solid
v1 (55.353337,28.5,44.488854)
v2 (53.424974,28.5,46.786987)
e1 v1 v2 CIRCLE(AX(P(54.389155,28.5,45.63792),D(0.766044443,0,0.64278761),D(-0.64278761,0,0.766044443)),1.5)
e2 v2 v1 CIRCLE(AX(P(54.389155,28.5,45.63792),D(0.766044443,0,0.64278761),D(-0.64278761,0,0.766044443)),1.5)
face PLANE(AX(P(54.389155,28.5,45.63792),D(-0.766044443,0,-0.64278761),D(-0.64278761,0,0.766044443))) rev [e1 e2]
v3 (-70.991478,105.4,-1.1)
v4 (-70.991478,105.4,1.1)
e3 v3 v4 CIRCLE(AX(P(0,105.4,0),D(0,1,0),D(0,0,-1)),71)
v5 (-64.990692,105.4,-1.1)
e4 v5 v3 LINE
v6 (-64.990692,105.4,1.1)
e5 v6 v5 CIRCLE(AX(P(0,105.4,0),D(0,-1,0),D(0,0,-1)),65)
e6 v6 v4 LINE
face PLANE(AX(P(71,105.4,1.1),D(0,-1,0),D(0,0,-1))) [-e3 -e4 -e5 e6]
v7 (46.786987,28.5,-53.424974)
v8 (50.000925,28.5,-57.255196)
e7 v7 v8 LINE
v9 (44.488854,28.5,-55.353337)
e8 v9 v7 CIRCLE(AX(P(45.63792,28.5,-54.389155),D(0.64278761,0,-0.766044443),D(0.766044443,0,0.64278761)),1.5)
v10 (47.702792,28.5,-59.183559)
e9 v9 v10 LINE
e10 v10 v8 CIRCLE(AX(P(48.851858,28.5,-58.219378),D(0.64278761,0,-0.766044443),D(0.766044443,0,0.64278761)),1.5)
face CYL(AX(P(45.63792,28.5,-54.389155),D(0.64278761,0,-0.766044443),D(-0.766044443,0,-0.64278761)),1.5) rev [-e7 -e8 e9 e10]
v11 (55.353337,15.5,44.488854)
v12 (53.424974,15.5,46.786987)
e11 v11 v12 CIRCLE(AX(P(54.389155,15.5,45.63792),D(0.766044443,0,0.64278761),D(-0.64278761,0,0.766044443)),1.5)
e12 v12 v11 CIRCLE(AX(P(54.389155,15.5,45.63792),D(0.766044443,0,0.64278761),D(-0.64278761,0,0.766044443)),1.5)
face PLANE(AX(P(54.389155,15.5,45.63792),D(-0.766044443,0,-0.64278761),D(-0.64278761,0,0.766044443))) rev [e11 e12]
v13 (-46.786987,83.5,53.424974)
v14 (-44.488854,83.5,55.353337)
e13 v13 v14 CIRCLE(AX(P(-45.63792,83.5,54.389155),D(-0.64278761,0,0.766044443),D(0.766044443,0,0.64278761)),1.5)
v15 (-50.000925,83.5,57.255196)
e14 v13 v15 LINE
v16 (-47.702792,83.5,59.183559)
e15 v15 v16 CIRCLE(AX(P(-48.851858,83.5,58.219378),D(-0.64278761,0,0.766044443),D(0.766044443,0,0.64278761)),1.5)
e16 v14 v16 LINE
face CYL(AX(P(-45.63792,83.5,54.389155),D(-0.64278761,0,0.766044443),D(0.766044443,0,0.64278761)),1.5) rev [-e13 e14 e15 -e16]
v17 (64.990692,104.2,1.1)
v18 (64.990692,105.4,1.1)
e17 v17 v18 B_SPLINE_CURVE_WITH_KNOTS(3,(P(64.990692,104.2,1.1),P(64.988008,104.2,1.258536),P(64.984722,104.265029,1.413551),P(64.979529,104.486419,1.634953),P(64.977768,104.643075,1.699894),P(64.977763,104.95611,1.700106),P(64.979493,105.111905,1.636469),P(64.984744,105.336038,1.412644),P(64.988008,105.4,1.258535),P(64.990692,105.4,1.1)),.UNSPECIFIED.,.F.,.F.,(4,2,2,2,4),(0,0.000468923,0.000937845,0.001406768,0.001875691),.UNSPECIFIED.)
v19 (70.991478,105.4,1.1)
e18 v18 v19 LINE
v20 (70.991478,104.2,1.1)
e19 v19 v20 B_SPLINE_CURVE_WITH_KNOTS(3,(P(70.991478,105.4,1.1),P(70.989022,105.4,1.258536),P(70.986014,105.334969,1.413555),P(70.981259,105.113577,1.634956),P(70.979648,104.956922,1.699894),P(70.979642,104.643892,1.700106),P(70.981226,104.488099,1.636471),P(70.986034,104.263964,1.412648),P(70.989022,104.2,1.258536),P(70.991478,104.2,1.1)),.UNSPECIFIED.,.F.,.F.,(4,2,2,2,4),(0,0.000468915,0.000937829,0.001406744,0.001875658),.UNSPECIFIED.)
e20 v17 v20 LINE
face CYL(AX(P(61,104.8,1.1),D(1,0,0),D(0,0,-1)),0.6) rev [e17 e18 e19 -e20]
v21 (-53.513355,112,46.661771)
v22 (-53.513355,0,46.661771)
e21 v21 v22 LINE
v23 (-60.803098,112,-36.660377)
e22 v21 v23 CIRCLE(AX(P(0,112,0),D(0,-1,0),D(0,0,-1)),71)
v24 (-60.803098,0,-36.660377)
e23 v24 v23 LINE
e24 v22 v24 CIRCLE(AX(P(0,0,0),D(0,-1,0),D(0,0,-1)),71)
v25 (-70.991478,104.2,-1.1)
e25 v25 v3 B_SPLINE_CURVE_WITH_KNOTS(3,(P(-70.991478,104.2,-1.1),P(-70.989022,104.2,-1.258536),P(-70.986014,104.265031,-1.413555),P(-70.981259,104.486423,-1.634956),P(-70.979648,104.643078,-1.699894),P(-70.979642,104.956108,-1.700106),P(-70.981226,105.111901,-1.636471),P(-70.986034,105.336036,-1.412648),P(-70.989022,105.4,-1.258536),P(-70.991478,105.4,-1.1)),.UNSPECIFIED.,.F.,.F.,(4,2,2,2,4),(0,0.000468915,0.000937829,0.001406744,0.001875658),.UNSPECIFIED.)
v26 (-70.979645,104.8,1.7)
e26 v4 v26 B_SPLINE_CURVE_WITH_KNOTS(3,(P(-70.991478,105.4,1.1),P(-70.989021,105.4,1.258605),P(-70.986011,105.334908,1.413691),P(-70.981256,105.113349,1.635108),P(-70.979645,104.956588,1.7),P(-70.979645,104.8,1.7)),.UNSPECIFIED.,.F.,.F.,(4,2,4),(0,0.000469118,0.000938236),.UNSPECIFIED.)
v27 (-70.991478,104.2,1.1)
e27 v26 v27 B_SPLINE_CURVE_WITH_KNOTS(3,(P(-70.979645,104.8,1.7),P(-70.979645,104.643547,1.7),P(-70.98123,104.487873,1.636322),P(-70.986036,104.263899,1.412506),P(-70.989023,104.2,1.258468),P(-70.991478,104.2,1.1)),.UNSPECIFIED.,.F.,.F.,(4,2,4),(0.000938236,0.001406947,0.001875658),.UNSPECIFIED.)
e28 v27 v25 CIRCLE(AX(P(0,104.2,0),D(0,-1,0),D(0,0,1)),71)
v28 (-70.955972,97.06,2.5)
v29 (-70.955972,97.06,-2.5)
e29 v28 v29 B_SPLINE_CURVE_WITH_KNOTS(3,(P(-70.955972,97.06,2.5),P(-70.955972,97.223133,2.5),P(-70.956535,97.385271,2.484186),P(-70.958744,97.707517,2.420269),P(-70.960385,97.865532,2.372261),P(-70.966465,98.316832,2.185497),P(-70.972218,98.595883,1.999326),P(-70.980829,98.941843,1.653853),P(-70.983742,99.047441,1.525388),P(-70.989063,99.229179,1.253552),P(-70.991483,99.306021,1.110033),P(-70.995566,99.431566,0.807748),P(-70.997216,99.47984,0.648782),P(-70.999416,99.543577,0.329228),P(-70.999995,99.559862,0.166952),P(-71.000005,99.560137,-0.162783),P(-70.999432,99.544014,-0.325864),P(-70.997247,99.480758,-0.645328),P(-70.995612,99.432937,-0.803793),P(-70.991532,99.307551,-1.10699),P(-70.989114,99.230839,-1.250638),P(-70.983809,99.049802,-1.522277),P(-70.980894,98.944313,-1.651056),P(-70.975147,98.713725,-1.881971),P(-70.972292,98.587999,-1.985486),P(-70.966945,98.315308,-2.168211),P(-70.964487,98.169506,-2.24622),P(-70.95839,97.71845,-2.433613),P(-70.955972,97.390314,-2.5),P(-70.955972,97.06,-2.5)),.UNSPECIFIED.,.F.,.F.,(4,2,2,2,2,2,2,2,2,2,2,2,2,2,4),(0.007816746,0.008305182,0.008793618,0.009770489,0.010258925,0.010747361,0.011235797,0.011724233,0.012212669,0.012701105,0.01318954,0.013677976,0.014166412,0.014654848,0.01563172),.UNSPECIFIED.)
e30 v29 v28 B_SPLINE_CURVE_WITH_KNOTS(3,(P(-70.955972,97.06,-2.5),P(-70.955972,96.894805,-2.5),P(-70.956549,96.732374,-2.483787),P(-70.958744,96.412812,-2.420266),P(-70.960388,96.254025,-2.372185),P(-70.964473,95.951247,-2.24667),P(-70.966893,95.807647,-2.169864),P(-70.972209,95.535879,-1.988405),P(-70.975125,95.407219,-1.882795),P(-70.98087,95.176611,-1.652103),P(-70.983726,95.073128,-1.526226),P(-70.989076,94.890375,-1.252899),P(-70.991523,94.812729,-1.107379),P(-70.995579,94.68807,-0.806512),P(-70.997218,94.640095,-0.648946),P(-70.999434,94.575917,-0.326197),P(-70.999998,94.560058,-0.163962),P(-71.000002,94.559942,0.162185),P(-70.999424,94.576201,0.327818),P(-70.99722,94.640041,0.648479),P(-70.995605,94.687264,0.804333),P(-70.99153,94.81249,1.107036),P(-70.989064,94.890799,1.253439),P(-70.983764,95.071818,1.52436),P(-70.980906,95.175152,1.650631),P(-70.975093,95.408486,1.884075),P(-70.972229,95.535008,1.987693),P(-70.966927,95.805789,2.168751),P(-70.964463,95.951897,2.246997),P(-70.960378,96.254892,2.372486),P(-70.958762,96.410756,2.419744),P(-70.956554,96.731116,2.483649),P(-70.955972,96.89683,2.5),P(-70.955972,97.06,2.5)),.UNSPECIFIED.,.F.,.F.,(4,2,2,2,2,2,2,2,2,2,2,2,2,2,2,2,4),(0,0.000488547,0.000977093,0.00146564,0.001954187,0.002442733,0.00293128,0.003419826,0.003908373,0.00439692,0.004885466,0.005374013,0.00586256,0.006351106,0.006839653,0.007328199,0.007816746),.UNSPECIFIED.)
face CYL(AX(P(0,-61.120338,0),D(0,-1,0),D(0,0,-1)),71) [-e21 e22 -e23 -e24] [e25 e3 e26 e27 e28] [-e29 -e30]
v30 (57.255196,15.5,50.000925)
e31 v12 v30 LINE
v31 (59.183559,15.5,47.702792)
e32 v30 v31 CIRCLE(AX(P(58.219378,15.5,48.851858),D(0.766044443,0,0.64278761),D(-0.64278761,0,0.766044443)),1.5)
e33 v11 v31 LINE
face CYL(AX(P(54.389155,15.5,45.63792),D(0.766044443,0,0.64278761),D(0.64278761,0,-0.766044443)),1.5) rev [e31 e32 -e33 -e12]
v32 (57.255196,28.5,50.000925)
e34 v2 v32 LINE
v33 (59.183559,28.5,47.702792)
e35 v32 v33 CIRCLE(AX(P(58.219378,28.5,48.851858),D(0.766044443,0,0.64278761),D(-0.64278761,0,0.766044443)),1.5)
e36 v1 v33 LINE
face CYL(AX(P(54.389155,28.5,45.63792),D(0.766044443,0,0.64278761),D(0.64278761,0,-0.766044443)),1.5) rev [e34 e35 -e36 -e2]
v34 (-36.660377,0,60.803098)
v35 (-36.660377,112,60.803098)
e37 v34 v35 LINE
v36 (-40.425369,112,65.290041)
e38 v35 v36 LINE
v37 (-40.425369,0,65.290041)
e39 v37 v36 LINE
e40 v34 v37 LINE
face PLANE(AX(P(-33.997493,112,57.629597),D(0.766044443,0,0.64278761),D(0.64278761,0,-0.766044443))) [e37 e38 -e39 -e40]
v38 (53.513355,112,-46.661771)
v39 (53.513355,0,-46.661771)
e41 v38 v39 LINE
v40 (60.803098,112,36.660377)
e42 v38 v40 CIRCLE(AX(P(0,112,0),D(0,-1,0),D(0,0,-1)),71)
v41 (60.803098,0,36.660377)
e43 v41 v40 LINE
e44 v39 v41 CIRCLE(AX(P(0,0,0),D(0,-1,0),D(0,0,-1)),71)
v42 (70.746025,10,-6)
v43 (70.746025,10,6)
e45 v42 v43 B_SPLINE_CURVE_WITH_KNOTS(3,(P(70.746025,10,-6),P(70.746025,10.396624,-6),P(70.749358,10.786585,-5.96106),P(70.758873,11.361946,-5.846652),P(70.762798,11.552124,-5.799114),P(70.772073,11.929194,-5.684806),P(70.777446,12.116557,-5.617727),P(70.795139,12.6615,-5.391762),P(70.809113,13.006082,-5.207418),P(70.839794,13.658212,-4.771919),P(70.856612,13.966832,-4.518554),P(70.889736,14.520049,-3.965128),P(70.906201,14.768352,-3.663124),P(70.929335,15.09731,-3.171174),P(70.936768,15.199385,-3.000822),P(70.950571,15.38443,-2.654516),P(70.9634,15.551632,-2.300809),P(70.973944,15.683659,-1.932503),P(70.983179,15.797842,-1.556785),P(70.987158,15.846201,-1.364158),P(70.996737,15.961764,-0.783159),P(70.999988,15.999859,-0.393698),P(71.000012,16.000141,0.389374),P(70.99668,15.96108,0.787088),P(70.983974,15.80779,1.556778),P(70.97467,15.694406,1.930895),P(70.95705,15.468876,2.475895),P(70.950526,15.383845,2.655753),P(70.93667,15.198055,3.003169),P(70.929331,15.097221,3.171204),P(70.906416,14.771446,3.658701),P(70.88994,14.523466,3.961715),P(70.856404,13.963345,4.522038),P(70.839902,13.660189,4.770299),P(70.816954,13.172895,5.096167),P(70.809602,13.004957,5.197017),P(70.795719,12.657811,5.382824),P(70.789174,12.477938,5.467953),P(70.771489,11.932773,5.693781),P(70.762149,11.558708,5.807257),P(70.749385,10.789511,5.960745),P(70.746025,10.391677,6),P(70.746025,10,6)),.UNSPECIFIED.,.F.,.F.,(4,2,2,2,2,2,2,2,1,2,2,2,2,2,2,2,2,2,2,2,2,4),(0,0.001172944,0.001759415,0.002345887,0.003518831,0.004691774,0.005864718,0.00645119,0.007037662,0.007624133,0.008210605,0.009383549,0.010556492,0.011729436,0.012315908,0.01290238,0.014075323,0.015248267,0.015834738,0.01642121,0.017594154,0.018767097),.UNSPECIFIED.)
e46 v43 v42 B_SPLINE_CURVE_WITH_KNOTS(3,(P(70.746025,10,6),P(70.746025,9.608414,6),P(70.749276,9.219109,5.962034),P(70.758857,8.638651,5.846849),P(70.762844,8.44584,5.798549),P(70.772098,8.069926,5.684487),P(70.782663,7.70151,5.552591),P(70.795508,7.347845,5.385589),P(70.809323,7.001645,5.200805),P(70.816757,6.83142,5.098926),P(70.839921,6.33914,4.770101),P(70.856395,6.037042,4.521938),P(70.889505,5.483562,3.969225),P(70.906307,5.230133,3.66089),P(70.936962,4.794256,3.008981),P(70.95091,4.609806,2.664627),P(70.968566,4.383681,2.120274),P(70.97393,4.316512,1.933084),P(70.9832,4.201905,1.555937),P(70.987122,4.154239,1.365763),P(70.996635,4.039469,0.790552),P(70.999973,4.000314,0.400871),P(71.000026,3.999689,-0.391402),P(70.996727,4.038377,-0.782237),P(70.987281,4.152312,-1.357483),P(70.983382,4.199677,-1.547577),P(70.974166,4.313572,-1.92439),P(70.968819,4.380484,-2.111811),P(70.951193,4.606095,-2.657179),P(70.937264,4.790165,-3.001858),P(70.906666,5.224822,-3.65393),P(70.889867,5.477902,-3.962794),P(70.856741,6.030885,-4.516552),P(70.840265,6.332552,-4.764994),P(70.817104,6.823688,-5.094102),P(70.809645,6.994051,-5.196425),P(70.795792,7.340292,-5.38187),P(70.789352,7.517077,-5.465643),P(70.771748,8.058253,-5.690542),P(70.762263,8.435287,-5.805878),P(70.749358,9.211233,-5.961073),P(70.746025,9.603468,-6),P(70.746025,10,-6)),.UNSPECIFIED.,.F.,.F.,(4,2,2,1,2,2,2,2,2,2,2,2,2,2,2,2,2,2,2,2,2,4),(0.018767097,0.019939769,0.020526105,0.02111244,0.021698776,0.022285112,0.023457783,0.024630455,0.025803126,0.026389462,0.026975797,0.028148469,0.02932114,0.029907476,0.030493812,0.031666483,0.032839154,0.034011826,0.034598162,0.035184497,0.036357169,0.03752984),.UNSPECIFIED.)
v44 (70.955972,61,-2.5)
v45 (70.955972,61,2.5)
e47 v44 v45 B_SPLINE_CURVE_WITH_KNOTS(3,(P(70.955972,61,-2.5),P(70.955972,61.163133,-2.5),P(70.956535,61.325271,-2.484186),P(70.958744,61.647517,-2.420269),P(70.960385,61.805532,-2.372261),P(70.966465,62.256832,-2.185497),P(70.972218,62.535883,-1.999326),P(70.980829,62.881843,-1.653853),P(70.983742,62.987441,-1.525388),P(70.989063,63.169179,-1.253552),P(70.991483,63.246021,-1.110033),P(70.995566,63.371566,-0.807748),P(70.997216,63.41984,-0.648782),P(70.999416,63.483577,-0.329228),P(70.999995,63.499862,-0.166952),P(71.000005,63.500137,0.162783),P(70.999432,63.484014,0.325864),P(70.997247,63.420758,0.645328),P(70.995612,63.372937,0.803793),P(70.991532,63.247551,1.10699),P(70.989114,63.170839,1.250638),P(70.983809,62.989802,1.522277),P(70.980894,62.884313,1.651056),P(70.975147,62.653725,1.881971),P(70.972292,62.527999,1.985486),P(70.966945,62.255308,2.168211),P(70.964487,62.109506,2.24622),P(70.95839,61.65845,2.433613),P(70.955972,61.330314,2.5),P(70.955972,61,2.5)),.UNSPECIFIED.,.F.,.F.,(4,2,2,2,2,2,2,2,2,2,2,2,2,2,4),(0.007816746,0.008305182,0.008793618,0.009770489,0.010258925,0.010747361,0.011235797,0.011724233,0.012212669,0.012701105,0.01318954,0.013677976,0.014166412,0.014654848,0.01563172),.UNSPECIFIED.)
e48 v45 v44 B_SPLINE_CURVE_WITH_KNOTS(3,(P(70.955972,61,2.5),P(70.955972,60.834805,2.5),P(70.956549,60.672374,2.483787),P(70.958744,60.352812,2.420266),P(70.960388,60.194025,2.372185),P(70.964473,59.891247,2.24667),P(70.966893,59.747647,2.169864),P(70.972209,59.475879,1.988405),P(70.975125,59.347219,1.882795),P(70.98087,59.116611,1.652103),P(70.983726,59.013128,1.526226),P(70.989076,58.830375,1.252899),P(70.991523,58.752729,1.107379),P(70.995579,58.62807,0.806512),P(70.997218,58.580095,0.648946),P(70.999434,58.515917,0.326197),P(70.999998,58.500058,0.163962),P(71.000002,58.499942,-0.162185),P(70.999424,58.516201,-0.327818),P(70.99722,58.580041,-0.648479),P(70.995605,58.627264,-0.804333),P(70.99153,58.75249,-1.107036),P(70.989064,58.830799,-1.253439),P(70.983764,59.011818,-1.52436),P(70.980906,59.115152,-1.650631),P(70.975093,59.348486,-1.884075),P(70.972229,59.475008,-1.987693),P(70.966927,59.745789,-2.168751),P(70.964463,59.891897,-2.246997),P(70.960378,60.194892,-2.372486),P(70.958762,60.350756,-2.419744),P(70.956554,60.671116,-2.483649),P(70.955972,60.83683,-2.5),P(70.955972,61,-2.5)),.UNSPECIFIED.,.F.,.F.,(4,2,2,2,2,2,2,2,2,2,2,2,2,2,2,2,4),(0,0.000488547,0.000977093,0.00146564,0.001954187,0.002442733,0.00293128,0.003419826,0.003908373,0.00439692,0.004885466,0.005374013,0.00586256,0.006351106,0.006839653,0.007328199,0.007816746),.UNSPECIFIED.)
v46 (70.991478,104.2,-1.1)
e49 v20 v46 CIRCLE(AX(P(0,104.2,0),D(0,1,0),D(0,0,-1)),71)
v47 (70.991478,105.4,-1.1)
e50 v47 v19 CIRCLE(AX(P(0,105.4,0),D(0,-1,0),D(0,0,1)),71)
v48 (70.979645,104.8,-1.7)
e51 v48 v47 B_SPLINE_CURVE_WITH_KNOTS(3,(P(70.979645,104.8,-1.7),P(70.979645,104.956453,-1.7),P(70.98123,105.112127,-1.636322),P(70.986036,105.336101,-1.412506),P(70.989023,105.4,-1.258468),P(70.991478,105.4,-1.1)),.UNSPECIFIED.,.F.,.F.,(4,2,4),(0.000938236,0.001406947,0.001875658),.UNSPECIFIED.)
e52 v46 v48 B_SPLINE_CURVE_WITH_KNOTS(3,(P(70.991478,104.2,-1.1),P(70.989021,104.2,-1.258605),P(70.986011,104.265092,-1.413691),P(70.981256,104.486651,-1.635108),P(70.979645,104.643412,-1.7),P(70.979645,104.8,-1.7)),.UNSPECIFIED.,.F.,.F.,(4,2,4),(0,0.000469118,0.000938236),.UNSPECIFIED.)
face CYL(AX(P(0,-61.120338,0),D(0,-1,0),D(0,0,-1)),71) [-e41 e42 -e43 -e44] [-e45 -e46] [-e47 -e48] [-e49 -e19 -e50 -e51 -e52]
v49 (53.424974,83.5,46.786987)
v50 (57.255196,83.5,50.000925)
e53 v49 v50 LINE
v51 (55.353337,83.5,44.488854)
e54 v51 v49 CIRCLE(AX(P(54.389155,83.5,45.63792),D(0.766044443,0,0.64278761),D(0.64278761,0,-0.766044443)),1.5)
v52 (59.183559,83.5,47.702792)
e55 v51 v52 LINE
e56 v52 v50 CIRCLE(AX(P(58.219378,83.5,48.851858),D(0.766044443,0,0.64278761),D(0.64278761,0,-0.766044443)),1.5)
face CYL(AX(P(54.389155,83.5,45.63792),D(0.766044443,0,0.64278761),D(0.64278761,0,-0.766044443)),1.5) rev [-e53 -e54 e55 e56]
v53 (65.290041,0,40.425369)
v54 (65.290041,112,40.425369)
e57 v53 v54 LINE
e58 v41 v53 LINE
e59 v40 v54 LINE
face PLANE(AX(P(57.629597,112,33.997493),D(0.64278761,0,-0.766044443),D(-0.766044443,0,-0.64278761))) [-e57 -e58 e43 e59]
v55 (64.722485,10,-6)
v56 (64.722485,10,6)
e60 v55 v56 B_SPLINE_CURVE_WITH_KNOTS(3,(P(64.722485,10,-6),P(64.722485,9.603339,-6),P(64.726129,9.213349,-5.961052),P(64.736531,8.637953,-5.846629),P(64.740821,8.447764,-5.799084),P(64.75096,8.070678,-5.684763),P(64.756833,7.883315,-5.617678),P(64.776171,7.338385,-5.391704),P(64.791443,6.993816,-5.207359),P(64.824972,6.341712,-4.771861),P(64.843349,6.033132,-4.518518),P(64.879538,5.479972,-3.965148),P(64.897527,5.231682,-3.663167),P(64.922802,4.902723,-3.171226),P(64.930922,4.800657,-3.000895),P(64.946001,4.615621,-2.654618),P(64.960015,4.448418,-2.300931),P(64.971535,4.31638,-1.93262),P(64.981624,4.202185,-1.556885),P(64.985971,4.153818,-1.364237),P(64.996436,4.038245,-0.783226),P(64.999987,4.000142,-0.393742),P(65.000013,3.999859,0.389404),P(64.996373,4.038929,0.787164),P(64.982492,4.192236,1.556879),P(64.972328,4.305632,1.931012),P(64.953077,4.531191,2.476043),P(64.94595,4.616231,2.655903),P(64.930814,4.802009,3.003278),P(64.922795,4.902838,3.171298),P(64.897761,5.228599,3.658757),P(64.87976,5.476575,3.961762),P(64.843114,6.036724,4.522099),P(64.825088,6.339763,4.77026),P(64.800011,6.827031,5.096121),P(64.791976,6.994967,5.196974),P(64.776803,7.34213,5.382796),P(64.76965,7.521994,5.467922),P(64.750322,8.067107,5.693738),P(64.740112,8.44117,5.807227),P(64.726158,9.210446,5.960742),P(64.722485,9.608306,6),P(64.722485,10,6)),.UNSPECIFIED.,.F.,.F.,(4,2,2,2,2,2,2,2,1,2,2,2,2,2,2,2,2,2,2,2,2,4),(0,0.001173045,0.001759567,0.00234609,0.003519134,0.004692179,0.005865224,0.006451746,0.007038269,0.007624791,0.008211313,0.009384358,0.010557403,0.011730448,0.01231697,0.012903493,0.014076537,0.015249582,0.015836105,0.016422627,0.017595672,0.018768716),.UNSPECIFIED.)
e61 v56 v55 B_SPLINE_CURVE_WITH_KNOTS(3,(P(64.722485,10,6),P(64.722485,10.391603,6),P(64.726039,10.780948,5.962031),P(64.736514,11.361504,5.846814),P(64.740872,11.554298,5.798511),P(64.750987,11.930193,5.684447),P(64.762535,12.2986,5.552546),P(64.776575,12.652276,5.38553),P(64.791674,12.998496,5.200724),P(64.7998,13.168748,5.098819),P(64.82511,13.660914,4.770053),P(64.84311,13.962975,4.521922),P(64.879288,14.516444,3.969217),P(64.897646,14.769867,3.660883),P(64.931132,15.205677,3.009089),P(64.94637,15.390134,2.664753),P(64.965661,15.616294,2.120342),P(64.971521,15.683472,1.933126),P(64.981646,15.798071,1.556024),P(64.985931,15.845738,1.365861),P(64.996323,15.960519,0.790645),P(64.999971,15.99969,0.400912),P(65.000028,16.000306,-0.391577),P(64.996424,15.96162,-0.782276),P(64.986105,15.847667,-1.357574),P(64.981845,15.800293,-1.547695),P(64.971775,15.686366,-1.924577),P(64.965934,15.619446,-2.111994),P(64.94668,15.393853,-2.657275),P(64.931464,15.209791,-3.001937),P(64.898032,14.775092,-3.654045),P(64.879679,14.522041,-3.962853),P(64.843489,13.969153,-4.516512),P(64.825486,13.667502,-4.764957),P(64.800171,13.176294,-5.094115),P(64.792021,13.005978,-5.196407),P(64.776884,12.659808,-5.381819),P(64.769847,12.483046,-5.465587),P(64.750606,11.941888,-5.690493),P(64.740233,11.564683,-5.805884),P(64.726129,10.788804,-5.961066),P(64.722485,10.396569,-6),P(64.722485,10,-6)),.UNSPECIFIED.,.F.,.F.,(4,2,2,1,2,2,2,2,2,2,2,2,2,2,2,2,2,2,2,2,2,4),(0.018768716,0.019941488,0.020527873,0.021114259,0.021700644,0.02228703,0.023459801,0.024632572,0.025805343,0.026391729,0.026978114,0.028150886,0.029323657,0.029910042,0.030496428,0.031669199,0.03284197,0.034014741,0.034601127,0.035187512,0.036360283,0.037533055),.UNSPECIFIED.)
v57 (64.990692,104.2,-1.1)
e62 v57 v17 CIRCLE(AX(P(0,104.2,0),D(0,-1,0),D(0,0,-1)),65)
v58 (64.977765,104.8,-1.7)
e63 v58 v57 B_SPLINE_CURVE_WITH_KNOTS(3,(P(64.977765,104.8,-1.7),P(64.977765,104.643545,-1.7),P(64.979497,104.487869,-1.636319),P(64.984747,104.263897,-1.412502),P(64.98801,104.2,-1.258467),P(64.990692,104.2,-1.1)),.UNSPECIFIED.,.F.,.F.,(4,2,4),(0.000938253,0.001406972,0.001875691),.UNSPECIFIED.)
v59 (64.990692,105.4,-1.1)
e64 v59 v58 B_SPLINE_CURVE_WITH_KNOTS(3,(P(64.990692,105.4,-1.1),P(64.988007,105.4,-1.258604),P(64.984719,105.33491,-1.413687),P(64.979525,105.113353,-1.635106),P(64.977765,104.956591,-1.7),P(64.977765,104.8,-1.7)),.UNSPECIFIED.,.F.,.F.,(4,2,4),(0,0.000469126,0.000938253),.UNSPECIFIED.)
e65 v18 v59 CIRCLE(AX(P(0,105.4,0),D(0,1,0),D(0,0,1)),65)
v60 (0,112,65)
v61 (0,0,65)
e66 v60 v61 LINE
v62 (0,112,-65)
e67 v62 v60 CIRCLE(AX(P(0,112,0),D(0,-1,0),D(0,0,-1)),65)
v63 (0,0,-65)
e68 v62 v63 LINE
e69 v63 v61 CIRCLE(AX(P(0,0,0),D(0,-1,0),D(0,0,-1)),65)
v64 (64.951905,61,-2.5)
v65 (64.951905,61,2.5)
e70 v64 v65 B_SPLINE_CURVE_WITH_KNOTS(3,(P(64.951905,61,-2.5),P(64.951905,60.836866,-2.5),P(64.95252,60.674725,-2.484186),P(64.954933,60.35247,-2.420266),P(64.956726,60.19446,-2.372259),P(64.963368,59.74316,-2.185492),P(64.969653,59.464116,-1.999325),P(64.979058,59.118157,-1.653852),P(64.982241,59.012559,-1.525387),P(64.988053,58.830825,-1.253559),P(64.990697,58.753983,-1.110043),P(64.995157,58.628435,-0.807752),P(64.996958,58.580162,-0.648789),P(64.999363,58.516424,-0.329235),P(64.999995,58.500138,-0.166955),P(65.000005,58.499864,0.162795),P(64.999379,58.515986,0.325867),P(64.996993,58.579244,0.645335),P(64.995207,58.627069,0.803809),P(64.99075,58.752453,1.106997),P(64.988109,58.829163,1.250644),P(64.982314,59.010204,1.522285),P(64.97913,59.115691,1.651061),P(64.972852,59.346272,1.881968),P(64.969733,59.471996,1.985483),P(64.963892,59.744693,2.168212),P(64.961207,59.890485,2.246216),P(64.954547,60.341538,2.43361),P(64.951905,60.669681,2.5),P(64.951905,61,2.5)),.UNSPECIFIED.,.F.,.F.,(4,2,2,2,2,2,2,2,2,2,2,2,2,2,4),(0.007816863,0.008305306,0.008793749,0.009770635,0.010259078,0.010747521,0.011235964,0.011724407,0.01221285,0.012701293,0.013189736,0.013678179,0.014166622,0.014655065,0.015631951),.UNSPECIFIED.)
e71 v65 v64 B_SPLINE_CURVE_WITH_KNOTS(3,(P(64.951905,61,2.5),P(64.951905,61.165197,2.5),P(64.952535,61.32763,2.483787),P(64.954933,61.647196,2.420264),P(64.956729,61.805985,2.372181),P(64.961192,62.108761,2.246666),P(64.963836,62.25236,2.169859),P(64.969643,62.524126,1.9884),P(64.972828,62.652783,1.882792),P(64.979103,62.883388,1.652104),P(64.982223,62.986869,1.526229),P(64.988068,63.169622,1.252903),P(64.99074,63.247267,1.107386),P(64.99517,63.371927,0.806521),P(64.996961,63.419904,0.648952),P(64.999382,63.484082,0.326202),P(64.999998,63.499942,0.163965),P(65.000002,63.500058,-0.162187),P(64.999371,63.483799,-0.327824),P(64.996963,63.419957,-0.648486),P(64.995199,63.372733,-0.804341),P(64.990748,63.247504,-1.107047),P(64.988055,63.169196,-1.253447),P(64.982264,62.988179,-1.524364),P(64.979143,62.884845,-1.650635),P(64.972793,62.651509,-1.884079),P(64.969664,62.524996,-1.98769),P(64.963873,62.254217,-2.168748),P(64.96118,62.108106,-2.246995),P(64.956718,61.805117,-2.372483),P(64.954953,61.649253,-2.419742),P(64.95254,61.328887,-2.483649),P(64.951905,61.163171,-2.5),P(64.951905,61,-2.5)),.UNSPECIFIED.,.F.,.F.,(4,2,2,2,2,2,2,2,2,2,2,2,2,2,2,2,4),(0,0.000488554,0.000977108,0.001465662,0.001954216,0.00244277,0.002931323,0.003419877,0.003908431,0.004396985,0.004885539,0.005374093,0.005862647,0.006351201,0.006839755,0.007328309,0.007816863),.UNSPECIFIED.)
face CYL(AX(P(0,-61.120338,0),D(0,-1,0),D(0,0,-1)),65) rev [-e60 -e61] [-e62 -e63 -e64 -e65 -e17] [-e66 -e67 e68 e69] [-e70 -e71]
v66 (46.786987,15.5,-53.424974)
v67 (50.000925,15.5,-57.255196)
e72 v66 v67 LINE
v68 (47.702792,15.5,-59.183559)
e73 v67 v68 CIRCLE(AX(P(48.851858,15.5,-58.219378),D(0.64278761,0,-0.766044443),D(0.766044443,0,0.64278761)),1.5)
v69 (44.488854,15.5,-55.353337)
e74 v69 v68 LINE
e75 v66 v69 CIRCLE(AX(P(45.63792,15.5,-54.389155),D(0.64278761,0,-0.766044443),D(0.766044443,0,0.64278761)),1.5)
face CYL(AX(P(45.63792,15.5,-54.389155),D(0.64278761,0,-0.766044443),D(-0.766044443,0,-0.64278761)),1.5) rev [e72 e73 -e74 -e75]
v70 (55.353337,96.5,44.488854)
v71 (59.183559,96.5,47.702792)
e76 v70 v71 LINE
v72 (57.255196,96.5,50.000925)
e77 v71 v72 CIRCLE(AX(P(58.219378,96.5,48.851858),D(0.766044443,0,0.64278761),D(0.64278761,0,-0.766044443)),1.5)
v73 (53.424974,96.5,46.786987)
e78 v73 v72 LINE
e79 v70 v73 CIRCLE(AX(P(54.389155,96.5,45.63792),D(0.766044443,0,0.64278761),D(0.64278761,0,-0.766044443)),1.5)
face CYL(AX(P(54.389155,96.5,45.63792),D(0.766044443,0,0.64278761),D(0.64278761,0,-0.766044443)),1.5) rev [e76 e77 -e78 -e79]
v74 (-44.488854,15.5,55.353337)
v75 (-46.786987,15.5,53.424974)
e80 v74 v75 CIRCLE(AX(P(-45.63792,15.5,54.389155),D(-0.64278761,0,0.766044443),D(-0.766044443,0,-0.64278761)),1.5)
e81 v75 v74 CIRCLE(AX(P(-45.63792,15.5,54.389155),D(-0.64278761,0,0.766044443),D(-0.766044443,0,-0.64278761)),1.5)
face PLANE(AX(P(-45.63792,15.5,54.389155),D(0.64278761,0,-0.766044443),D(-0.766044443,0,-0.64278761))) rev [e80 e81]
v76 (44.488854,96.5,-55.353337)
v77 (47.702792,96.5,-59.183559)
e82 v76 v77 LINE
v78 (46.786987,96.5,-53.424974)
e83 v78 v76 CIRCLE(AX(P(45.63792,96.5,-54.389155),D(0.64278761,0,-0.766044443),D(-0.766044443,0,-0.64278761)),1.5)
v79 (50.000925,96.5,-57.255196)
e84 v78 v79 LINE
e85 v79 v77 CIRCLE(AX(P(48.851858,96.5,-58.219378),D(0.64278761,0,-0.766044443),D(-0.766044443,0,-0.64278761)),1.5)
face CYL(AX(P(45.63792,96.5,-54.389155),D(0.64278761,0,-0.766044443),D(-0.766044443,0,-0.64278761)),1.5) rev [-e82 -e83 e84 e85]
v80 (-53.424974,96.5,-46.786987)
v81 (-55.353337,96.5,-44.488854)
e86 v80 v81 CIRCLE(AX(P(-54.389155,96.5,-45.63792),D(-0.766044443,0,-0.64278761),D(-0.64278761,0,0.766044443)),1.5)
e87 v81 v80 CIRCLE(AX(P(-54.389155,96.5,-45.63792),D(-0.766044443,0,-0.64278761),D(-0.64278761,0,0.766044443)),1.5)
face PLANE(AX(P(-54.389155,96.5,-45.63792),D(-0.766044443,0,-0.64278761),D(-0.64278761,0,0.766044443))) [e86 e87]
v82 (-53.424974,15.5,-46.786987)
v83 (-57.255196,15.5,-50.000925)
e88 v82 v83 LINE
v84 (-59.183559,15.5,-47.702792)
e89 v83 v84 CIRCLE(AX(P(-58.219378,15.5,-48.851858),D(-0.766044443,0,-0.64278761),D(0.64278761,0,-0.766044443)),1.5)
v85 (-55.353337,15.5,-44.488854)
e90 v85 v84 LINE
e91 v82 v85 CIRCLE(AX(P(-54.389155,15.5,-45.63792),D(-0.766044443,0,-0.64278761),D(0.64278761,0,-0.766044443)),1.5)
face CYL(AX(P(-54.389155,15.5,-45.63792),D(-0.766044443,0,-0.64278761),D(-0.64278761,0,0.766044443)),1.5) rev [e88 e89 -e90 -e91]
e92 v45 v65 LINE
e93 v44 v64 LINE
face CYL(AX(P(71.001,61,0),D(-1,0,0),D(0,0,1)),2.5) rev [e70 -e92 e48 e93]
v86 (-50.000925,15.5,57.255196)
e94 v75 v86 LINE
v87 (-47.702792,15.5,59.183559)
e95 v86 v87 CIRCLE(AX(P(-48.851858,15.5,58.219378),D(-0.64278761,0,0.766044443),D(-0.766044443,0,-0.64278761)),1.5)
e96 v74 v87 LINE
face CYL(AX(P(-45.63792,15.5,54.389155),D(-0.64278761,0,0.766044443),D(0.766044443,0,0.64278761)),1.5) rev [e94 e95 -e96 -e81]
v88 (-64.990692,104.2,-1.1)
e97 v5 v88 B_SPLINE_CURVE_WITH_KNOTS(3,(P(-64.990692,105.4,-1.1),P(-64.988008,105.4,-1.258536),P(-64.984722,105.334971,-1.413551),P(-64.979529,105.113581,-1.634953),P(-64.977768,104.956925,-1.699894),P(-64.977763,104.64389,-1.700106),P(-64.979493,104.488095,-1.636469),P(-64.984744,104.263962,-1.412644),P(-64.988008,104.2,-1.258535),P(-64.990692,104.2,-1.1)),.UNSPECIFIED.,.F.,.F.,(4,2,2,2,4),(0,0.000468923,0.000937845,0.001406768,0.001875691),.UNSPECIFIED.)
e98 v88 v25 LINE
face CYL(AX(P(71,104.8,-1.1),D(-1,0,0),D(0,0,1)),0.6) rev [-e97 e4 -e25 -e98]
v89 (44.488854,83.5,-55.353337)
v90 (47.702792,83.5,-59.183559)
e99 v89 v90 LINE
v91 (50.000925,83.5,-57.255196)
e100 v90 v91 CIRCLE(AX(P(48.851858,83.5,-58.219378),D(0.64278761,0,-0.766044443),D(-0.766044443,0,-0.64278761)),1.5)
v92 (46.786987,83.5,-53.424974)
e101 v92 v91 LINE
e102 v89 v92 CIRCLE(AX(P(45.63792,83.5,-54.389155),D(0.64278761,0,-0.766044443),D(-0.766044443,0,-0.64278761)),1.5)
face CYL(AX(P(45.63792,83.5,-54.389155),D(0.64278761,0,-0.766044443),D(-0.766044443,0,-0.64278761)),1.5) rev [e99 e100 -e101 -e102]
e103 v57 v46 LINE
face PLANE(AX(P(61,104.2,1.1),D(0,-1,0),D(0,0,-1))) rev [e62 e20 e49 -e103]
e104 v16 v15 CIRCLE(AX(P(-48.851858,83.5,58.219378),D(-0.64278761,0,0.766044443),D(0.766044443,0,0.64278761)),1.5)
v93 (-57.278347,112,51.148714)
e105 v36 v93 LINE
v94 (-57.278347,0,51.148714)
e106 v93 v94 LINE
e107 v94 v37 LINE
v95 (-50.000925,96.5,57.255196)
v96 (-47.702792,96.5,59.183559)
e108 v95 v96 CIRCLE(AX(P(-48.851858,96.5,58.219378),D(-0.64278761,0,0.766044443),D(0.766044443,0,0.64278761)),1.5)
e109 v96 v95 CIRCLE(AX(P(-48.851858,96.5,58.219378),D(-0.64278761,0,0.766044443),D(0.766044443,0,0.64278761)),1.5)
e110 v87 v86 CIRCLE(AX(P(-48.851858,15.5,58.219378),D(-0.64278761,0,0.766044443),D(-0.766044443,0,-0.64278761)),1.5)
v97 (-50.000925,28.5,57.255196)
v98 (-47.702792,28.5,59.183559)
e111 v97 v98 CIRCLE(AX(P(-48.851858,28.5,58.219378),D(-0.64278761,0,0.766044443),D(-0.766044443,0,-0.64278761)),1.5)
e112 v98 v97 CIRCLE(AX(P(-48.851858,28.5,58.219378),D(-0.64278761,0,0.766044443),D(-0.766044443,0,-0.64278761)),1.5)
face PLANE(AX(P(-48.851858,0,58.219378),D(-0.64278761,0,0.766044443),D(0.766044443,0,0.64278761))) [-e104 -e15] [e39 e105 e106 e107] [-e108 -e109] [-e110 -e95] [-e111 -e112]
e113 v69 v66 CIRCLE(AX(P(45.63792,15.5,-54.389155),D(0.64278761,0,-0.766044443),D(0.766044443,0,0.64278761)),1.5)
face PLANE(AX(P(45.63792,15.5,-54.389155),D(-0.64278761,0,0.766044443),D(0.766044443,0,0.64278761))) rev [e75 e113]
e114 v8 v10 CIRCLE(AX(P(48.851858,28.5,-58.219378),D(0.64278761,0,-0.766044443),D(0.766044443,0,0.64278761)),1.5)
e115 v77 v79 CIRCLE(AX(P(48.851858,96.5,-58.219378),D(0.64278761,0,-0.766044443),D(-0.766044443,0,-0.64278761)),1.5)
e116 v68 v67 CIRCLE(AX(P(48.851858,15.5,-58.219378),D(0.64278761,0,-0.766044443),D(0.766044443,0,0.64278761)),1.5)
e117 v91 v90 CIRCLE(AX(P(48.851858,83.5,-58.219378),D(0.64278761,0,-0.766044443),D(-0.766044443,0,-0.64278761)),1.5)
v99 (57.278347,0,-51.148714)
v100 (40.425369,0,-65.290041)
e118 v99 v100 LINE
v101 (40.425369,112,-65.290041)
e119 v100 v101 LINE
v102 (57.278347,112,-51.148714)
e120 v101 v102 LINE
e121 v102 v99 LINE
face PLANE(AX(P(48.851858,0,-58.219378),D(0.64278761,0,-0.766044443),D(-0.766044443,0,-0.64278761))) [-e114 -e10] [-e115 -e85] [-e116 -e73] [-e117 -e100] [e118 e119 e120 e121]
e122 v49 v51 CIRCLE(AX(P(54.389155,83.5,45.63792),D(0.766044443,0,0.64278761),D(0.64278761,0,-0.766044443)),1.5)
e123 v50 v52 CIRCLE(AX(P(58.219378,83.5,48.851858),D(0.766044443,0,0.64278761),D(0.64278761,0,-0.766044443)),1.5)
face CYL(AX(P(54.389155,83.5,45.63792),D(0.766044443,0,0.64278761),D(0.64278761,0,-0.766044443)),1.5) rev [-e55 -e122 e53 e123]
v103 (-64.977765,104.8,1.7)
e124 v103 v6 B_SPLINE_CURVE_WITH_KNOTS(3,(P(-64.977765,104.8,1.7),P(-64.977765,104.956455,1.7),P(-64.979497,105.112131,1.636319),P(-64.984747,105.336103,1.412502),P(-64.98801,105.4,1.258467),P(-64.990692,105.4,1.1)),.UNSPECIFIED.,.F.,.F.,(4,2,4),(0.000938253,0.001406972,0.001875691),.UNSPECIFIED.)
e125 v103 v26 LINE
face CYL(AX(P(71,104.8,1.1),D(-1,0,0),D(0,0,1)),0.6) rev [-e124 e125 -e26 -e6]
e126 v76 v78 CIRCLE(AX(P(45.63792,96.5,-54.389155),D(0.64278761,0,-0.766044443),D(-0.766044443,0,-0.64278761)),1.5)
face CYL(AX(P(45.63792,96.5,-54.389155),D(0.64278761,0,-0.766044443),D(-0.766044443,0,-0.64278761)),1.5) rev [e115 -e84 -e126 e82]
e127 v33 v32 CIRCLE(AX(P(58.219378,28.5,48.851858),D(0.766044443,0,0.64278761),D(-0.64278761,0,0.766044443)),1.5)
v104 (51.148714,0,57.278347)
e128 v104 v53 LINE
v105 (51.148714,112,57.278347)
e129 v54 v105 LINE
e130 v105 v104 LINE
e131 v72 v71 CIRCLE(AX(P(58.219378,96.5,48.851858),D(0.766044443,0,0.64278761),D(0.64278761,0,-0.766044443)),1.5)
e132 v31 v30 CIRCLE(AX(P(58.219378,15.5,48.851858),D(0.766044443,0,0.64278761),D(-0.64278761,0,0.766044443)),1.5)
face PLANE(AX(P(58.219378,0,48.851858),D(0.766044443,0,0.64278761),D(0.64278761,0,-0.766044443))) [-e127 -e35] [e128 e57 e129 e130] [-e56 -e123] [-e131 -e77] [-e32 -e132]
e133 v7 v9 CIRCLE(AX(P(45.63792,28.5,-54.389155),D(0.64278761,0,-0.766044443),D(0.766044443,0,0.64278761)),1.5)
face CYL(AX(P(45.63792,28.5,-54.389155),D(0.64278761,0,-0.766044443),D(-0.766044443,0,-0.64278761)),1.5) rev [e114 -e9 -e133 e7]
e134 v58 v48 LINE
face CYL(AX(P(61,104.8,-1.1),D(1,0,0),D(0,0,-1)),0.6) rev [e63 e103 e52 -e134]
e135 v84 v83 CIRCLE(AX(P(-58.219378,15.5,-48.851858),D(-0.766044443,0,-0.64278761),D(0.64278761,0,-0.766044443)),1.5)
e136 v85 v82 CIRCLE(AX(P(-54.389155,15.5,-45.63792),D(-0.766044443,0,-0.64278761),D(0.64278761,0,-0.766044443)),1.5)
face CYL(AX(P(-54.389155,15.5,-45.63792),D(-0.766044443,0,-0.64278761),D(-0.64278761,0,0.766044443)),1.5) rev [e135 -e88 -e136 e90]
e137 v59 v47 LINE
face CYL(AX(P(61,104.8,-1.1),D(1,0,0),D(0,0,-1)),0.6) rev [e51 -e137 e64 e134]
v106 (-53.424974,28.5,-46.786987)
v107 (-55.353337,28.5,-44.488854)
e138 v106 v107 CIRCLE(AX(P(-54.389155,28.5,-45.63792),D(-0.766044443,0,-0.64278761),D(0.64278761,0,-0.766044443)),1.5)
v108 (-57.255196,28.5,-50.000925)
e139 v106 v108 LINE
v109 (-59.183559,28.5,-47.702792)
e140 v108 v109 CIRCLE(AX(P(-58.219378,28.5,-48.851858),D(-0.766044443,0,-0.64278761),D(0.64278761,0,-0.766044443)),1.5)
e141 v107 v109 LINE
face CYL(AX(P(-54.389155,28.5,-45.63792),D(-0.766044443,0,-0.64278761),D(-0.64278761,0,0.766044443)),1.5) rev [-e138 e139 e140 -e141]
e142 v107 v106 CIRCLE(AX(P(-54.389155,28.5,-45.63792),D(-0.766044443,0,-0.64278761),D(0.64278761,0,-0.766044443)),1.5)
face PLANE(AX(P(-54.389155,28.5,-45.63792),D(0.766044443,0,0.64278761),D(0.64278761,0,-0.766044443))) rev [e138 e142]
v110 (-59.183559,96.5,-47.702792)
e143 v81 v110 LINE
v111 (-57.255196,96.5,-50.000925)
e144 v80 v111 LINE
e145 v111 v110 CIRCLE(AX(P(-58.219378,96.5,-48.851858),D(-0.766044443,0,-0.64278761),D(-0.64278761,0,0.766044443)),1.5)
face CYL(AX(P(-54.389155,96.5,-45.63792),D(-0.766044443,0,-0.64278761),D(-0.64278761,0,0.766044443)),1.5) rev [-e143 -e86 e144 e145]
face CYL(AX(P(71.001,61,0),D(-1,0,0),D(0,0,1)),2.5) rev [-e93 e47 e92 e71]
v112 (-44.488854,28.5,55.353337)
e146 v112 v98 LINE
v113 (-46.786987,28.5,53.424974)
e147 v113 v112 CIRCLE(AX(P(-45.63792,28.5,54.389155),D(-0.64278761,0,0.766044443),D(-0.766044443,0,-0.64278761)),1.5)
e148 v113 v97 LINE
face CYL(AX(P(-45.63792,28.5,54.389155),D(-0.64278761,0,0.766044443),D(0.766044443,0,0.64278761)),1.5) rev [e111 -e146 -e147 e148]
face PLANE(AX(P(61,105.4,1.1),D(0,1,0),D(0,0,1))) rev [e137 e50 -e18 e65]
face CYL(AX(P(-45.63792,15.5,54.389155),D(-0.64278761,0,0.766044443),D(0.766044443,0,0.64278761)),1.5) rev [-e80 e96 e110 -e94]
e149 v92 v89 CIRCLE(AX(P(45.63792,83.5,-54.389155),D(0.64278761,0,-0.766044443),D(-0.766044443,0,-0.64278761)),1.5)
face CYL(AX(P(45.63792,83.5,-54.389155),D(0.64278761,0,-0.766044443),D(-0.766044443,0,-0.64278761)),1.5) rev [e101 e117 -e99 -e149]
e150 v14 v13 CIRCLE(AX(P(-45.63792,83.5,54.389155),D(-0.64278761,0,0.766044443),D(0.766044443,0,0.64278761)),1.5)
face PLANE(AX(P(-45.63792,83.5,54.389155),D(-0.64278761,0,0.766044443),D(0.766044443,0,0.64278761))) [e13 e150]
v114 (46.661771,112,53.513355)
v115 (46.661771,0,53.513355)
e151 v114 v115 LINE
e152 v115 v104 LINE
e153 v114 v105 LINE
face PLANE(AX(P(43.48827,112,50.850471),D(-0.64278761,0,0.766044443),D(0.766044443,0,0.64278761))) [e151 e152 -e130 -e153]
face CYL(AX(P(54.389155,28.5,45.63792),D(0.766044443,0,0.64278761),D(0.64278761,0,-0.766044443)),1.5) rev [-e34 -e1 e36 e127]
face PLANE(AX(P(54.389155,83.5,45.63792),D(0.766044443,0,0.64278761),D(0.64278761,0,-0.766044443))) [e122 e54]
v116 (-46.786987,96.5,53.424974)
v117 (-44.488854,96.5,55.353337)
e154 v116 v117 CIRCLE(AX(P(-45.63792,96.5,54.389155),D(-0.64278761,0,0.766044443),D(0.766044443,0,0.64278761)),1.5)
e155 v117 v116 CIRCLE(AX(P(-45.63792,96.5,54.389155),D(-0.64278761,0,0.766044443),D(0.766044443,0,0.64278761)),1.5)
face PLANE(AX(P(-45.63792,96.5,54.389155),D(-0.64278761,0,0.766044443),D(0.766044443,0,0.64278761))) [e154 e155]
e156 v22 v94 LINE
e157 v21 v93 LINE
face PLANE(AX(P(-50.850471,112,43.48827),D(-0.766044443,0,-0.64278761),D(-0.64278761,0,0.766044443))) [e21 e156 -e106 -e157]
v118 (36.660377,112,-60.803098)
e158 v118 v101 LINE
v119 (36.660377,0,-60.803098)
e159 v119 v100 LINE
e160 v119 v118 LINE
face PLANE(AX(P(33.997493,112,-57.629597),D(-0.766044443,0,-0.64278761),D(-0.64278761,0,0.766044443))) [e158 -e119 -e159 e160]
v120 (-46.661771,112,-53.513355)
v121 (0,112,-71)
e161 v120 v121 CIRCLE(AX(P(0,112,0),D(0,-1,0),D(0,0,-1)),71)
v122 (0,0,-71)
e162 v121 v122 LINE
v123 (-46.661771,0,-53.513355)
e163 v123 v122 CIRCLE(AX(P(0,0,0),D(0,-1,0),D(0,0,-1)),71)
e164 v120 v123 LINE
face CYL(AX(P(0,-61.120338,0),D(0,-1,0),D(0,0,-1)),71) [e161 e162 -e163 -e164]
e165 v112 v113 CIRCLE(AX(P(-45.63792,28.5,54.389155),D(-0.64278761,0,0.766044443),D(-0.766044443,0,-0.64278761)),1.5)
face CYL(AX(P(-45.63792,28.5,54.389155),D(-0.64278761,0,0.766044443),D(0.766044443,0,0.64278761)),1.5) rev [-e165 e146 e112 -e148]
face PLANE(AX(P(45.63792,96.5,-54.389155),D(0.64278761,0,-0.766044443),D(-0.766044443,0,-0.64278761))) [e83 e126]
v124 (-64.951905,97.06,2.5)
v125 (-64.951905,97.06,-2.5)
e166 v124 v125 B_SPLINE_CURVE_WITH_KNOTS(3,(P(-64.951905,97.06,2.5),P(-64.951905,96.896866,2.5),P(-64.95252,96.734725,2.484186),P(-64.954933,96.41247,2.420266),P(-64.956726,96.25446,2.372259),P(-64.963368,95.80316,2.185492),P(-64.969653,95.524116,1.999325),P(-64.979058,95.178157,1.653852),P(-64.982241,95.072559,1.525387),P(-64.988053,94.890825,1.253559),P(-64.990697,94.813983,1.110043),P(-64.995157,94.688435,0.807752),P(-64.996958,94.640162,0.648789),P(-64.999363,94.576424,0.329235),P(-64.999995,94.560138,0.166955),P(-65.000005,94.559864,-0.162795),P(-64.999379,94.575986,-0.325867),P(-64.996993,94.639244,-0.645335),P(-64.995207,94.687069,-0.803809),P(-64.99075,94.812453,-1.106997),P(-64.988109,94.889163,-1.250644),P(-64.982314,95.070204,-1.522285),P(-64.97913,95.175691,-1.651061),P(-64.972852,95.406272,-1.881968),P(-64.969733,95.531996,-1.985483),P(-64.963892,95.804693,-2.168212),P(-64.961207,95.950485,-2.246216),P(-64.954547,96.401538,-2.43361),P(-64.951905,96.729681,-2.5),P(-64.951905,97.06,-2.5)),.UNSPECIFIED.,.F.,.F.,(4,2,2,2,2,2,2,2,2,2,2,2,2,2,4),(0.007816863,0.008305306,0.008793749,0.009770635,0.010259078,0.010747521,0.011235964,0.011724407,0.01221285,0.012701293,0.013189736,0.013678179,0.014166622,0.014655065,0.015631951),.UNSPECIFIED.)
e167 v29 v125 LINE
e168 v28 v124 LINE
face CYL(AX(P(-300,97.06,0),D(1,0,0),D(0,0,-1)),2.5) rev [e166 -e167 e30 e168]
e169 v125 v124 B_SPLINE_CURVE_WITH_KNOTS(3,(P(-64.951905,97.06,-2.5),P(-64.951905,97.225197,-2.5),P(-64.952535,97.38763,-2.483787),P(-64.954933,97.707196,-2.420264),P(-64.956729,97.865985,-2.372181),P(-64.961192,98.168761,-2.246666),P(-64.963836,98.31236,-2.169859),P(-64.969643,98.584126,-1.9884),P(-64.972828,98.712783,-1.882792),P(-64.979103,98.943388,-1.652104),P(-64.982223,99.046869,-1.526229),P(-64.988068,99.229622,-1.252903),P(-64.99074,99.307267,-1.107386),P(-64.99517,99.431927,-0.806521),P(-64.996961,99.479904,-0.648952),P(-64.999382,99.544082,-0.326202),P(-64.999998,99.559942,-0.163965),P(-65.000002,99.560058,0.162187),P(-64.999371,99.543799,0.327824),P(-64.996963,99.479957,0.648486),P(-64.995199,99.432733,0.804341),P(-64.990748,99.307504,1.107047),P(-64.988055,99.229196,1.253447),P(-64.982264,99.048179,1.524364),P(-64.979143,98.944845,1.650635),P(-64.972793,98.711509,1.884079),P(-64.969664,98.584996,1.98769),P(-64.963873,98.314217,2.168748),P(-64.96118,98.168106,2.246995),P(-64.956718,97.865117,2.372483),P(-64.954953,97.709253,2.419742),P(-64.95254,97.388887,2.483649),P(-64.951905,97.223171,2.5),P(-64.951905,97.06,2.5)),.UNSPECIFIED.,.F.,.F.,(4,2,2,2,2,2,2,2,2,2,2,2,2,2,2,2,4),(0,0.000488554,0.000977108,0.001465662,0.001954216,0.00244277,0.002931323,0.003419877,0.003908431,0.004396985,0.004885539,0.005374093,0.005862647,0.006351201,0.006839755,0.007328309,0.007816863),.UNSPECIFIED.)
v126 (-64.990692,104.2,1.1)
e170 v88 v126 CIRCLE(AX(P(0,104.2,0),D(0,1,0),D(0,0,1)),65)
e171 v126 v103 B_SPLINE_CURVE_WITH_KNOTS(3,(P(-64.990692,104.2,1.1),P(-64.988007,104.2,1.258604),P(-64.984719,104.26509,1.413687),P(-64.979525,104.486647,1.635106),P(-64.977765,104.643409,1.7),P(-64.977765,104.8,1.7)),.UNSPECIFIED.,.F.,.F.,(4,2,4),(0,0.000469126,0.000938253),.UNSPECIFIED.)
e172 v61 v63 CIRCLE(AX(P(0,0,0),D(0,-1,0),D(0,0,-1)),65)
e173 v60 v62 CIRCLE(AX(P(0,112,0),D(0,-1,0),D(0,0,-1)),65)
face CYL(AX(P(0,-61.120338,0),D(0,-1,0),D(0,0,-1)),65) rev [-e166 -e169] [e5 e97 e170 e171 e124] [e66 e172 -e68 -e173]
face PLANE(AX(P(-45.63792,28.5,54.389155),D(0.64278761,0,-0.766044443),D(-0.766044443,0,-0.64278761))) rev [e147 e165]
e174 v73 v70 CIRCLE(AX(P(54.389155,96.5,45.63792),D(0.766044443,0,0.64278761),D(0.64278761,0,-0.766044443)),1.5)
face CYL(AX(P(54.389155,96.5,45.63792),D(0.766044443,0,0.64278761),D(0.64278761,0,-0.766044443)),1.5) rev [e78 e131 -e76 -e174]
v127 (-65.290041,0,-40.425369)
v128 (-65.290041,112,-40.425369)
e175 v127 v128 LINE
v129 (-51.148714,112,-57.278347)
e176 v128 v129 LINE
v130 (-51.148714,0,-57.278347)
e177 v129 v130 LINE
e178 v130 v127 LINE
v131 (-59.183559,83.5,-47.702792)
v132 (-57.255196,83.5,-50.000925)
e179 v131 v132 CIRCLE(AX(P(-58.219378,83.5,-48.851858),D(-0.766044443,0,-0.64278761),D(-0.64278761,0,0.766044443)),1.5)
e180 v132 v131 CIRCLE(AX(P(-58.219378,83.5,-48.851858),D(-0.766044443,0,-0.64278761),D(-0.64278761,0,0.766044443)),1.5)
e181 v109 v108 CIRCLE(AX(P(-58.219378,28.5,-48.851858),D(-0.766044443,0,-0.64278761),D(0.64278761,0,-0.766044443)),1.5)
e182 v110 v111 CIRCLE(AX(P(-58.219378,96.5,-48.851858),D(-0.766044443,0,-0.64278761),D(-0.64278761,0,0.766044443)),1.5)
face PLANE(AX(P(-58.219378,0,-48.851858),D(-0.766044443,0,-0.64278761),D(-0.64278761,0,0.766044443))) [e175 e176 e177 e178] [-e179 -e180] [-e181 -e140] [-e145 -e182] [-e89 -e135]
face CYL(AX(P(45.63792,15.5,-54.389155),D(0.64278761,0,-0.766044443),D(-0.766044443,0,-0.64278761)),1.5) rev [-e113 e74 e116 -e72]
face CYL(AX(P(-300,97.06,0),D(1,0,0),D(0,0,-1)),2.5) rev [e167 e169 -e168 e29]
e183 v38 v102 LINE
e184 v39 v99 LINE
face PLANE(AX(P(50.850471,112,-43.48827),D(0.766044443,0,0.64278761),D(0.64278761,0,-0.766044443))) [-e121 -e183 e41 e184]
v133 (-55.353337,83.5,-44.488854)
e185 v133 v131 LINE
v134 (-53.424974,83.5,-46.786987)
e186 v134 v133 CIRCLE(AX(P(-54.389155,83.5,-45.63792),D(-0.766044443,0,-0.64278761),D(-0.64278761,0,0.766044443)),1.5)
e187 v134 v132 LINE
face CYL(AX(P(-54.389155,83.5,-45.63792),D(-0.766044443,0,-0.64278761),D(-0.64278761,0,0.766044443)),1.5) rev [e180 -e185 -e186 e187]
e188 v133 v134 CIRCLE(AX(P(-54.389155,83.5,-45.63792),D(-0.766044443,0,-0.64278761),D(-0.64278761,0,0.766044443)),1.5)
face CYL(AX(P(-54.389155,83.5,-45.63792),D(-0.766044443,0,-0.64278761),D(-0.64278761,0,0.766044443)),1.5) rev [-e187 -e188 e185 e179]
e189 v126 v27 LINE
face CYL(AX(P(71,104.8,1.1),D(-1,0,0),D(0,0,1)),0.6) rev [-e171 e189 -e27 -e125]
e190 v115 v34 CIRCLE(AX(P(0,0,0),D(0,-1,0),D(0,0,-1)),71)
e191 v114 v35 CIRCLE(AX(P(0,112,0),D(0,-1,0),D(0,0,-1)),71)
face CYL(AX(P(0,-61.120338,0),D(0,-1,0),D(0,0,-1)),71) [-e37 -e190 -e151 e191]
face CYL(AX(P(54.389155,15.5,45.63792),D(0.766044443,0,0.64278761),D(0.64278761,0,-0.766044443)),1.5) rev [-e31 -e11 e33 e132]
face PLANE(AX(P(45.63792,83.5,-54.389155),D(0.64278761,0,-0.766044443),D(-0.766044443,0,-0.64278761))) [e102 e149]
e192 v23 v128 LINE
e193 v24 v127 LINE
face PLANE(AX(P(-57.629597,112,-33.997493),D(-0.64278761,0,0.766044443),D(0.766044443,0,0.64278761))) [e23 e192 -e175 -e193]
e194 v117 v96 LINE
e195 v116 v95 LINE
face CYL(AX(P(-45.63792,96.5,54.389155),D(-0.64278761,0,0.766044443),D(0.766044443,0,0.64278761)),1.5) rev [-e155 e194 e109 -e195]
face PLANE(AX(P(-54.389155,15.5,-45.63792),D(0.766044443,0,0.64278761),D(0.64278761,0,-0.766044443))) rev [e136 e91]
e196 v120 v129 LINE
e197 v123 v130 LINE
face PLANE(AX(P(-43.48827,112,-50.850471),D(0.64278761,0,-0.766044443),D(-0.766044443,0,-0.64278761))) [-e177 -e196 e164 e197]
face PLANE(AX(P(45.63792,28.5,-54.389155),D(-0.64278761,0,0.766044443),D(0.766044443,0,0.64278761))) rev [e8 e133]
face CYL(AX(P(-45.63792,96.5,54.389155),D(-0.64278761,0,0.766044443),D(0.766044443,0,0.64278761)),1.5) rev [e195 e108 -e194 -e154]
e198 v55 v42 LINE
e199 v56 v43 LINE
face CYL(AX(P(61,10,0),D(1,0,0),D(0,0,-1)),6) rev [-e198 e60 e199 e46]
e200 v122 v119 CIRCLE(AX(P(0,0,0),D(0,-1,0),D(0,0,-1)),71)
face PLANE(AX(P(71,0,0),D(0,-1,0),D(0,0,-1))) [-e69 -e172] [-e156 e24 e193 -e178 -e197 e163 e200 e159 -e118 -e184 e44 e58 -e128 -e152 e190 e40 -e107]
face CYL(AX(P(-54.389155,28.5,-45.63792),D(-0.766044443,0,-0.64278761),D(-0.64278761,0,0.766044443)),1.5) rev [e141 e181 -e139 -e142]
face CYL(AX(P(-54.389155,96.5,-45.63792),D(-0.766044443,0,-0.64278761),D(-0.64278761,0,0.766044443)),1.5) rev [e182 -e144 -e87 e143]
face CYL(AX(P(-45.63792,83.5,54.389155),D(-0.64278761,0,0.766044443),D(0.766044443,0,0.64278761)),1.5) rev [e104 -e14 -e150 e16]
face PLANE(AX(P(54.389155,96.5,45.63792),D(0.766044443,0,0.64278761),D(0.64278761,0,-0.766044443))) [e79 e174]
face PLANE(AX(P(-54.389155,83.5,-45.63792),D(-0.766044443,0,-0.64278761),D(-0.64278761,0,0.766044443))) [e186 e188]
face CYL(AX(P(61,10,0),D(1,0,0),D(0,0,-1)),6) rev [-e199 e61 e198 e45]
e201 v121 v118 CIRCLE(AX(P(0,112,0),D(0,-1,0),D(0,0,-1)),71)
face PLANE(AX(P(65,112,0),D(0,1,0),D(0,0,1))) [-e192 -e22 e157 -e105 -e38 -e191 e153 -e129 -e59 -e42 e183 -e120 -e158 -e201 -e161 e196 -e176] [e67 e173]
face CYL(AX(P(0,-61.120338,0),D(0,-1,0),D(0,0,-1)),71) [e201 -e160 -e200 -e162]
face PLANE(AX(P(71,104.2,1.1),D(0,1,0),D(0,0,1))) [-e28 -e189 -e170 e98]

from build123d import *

# Parameters (mm, degrees)
SKETCH1_W                = 6
SKETCH1_H                = 112
CUT_EXTRUDE1_DEPTH       = 10
SKETCH3_R                = 6
CUT_EXTRUDE2_DEPTH       = 10
CUT_EXTRUDE5_DEPTH       = 195.291019003
CUT_EXTRUDE5_DEPTH_BACK  = 195.291019003
SKETCH_5_4_R             = 2.5
CUT_EXTRUDE6_DEPTH       = 300
BOSS_EXTRUDE3_START      = 71
SKETCH10_W               = 112
SKETCH10_H               = 22
BOSS_EXTRUDE3_DEPTH      = 5
SKETCH12_R               = 1.5
CUT_EXTRUDE10_DEPTH      = 5
CIRPATTERN14_COUNT       = 4
CUT_EXTRUDE12_REACH      = 152.419
CUT_EXTRUDE12_END_RADIUS = 71
SKETCH_5_4_2_R           = 2.5


with BuildPart() as part:
    # Sketch1 → Revolve1 (revolve)
    with BuildSketch(Plane.XY, mode=Mode.PRIVATE) as revolve1_sk:
        with Locations((68, 56)):
            Rectangle(SKETCH1_W, SKETCH1_H)
    revolve(revolve1_sk.sketch.rotate(Axis((0, -61.12033846, 0), (0, 1, 0)), 90), axis=Axis((0, -61.12033846, 0), (0, 1, 0)))

    # Sketch2 → Cut-Extrude1 (cut)
    with BuildSketch(Plane(origin=(71, 0, 0), x_dir=(0, 0, -1), z_dir=(1, 0, 0))):
        with BuildLine():
            Line((-1.1, 105.4), (1.1, 105.4))
            ThreePointArc((1.1, 105.4), (1.7, 104.8), (1.1, 104.2))
            Line((1.1, 104.2), (-1.1, 104.2))
            ThreePointArc((-1.1, 104.2), (-1.7, 104.8), (-1.1, 105.4))
        make_face()
    extrude(amount=-CUT_EXTRUDE1_DEPTH, mode=Mode.SUBTRACT)

    # Sketch3 → Cut-Extrude2 (cut)
    with BuildSketch(Plane(origin=(71, 0, 0), x_dir=(0, 0, -1), z_dir=(1, 0, 0))):
        with Locations((0, 10)):
            Circle(SKETCH3_R)
    extrude(amount=-CUT_EXTRUDE2_DEPTH, mode=Mode.SUBTRACT)

    # Sketch4 → Cut-Extrude5 (cut, two sides: drawn at the far end of the back side and taken through both)
    with BuildSketch(Plane(origin=(-71, 0, 0), x_dir=(0, 0, -1), z_dir=(1, 0, 0)).offset(-CUT_EXTRUDE5_DEPTH_BACK)):
        with BuildLine():
            Line((-1.1, 105.4), (1.1, 105.4))
            ThreePointArc((1.1, 105.4), (1.7, 104.8), (1.1, 104.2))
            Line((1.1, 104.2), (-1.1, 104.2))
            ThreePointArc((-1.1, 104.2), (-1.7, 104.8), (-1.1, 105.4))
        make_face()
    extrude(amount=CUT_EXTRUDE5_DEPTH + CUT_EXTRUDE5_DEPTH_BACK, mode=Mode.SUBTRACT)

    # Sketch 5_4 → Cut-Extrude6 (cut)
    with BuildSketch(Plane(origin=(0, 0, 0), x_dir=(0, 0, -1), z_dir=(1, 0, 0))):
        with Locations((0, 97.06)):
            Circle(SKETCH_5_4_R)
    extrude(amount=-CUT_EXTRUDE6_DEPTH, mode=Mode.SUBTRACT)

    # Sketch10 → Boss-Extrude3 (add, symmetric)
    with BuildSketch(Plane(origin=(0, 0, 0), x_dir=(0, -1, 0), z_dir=(-0.7660444431189771, 0, -0.6427876096865406)).offset(BOSS_EXTRUDE3_START)):
        with Locations((-56, 0)):
            Rectangle(SKETCH10_W, SKETCH10_H)
    boss_extrude3 = extrude(amount=BOSS_EXTRUDE3_DEPTH, both=True)

    # Sketch12 → Cut-Extrude10 (cut)
    with BuildSketch(Plane(origin=(-58.219377677, 0, -48.851858336), x_dir=(-0.6427876096865407, 0, 0.766044443118977), z_dir=(-0.766044443118977, 0, -0.6427876096865407))):
        with Locations((0, 96.5)):
            Circle(SKETCH12_R)
        with Locations((0, 83.5)):
            Circle(SKETCH12_R)
        with Locations(Location((0, 28.5, 0), (0, 0, 180))):
            Circle(SKETCH12_R)
        with Locations(Location((0, 15.5, 0), (0, 0, 180))):
            Circle(SKETCH12_R)
    cut_extrude10 = extrude(amount=-CUT_EXTRUDE10_DEPTH, mode=Mode.SUBTRACT)

    # CirPattern14: Boss-Extrude3, Cut-Extrude10 ×4 about axis
    cirpattern14_axis = Axis((0, 0, 0), (0, 1, 0))
    add([boss_extrude3.rotate(cirpattern14_axis, i * 360 / CIRPATTERN14_COUNT) for i in range(1, CIRPATTERN14_COUNT)])
    add([cut_extrude10.rotate(cirpattern14_axis, i * 360 / CIRPATTERN14_COUNT) for i in range(1, CIRPATTERN14_COUNT)], mode=Mode.SUBTRACT)

    # Cut-Extrude12: up to this cylinder (the profile starts inside it)
    cut_extrude12_end = Plane(origin=(0, 61, 0), z_dir=(0, -1, 0)) * Cylinder(CUT_EXTRUDE12_END_RADIUS, 447.838, mode=Mode.PRIVATE)
    # Sketch 5_4 2 → Cut-Extrude12 (cut, up to the surface)
    with BuildSketch(Plane(origin=(0, 0, 0), x_dir=(0, 0, -1), z_dir=(1, 0, 0)), mode=Mode.PRIVATE) as cut_extrude12_sk1:
        with Locations(Location((0, 61, 0), (0, 0, 180))):
            Circle(SKETCH_5_4_2_R)
    cut_extrude12_tool1 = extrude(cut_extrude12_sk1.sketch, amount=CUT_EXTRUDE12_REACH, mode=Mode.PRIVATE) & cut_extrude12_end
    add(cut_extrude12_tool1.solids().sort_by_distance((0, 61, 0))[0], mode=Mode.SUBTRACT)


solid = part.part
